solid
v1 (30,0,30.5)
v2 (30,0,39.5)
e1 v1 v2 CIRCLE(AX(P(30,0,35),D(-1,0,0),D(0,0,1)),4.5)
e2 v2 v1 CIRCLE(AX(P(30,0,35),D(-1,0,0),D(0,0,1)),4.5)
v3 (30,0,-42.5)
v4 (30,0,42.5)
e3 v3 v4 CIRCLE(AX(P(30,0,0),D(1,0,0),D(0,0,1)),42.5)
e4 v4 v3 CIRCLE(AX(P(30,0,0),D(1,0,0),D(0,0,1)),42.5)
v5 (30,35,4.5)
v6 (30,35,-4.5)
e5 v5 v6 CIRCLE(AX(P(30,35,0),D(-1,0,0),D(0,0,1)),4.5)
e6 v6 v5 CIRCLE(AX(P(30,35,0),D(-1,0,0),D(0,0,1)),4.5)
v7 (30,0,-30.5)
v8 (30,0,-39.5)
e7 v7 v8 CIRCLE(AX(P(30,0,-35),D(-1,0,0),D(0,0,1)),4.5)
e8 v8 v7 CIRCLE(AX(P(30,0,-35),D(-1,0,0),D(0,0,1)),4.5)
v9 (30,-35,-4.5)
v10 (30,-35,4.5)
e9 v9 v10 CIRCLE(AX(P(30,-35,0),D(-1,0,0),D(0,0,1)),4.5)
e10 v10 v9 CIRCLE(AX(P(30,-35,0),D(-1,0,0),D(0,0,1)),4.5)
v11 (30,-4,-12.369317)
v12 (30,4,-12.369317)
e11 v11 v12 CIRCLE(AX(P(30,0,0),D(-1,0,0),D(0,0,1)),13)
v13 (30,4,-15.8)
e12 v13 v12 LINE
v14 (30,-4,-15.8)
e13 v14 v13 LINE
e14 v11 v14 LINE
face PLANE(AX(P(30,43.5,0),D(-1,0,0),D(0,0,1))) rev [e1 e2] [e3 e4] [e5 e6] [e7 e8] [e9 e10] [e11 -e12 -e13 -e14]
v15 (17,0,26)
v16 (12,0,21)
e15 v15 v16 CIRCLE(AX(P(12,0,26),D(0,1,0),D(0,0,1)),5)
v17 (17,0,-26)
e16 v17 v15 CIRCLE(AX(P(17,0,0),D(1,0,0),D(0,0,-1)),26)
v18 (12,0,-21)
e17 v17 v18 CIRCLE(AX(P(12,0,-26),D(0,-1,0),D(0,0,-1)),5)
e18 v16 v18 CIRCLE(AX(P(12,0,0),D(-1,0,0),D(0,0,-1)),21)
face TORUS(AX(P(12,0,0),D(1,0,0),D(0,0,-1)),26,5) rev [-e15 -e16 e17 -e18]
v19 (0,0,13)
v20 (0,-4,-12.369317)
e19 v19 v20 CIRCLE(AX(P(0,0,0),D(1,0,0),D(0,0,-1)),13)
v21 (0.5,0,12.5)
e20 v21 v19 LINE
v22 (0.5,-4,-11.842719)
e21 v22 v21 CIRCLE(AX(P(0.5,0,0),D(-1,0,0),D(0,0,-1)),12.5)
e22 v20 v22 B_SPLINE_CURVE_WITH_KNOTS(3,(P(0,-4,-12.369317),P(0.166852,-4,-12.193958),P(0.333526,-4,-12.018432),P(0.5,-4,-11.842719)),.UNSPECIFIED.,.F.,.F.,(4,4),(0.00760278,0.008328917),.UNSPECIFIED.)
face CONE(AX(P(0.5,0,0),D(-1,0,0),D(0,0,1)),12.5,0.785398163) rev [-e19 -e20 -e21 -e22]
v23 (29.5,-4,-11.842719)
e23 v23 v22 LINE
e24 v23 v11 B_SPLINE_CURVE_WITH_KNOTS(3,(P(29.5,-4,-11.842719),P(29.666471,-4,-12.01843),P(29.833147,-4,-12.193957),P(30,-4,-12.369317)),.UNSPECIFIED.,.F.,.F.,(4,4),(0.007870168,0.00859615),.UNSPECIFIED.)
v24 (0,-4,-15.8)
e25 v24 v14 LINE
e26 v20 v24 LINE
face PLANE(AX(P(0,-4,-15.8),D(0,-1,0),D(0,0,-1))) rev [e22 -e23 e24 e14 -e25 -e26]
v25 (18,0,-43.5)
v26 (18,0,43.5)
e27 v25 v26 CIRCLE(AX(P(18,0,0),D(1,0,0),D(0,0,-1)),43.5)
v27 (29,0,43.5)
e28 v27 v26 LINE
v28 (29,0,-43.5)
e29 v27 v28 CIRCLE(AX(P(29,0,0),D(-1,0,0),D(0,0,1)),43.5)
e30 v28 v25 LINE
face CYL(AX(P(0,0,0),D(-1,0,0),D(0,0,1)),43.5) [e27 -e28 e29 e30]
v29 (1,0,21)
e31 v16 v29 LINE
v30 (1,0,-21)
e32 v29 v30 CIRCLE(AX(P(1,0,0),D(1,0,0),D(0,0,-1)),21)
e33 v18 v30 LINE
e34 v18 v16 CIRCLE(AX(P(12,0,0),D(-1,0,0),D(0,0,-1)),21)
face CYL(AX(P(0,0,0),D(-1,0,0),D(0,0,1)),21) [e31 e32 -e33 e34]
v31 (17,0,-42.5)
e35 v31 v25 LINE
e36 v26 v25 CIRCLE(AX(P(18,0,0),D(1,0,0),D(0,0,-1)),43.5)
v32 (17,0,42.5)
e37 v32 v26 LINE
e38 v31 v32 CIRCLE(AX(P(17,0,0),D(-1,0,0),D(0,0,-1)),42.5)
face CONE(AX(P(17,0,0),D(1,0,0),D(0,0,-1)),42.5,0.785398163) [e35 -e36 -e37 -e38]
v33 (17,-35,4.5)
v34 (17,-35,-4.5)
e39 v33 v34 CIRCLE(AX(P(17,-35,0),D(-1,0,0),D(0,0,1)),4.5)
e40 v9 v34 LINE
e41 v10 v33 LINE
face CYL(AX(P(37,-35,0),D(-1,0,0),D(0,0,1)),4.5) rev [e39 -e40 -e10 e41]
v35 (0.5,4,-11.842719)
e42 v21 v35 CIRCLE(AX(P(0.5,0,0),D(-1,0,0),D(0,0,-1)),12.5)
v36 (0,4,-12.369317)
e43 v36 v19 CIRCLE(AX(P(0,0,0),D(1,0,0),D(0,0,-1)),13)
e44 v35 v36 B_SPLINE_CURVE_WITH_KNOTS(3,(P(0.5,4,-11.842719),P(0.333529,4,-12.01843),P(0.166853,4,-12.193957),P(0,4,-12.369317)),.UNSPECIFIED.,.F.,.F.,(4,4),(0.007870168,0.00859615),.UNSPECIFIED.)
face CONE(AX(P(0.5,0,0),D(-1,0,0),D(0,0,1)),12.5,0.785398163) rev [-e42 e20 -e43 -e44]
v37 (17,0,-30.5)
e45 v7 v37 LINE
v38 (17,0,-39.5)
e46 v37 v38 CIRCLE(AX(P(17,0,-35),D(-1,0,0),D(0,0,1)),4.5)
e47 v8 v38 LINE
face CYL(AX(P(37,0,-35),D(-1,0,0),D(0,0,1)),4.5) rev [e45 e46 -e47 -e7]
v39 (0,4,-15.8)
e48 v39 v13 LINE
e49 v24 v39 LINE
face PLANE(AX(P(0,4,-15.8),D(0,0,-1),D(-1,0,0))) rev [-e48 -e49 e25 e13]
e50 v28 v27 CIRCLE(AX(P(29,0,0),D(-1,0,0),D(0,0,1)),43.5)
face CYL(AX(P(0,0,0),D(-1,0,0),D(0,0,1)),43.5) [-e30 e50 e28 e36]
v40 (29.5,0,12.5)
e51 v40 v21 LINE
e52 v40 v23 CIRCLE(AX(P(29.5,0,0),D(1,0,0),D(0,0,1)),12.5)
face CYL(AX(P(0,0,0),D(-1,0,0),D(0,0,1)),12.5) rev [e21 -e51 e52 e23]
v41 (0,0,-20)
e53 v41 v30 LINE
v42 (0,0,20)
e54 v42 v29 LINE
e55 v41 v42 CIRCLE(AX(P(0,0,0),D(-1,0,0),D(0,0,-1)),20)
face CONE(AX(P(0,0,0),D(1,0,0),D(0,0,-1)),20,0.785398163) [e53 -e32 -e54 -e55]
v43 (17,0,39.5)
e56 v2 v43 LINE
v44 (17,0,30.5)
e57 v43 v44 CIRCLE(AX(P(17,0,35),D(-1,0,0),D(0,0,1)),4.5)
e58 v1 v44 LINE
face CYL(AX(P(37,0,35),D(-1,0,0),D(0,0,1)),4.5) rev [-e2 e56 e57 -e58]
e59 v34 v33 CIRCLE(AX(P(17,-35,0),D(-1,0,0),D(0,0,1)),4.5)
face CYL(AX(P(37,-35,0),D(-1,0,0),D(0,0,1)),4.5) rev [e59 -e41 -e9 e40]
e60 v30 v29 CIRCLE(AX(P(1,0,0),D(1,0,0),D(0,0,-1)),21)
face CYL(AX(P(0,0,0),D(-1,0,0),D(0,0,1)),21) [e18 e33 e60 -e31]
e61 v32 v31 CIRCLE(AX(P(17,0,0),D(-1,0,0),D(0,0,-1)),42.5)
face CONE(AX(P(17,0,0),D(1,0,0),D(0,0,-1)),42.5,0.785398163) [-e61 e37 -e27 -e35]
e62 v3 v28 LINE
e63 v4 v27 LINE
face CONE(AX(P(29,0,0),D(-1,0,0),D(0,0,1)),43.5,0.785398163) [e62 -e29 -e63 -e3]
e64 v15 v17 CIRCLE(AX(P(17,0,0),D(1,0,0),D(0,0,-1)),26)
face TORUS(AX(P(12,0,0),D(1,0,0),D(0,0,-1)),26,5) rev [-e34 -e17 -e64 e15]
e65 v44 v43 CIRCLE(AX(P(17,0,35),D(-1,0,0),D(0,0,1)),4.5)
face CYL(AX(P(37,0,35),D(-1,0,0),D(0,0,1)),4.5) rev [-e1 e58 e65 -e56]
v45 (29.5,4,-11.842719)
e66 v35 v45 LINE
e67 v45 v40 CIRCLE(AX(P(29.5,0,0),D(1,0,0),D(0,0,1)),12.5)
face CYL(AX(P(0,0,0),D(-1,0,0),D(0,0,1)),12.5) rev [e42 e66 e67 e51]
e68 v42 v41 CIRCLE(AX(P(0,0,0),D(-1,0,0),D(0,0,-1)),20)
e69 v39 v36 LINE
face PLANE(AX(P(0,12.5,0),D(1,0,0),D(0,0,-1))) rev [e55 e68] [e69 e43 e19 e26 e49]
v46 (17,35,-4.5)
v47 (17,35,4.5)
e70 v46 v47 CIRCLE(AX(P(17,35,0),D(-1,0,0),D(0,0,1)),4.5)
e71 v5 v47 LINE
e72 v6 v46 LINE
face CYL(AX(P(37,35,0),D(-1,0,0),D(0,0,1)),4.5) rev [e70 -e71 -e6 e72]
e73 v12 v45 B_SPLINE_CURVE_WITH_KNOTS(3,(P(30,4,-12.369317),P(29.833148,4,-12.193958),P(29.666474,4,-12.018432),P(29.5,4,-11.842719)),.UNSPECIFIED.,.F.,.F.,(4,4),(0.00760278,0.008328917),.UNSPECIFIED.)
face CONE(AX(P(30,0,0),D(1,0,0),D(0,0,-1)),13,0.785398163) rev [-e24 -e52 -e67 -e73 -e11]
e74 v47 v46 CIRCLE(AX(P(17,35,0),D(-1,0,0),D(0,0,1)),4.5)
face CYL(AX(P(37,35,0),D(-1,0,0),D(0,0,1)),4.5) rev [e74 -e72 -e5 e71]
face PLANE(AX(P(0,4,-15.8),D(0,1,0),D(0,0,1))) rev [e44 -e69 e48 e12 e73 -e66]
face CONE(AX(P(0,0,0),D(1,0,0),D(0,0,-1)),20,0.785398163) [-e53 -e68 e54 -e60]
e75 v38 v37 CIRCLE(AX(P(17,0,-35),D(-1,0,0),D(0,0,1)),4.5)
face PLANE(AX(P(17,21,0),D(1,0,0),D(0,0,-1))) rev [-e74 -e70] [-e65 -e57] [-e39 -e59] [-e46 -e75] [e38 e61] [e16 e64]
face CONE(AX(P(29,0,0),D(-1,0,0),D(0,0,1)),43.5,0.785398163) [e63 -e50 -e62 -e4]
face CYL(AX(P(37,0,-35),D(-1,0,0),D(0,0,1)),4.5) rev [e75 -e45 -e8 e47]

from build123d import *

# Parameters (mm, degrees)
CHAMFER1_SIZE      = 1
CHAMFER2_SIZE      = 0.5
FILLET1_R          = 5
CHAMFER3_SIZE      = 1
SKETCH2_R          = 4.5
CUT_EXTRUDE1_DEPTH = 20
SKETCH3_W          = 8.058064516
SKETCH3_H          = 8
CUT_EXTRUDE2_DEPTH = 69.443407279


with BuildPart() as part:
    # Sketch1 → Revolve1 (revolve)
    with BuildSketch(Plane.XY, mode=Mode.PRIVATE) as revolve1_sk:
        Polygon((0, 12.5), (0, 21), (17, 21), (17, 43.5), (30, 43.5), (30, 12.5), align=None)
    revolve(revolve1_sk.sketch.rotate(Axis((0, 0, 0), (1, 0, 0)), 90), axis=Axis((0, 0, 0), (1, 0, 0)))

    # Chamfer1
    chamfer1_edges = [part.edges().sort_by_distance(p)[0] for p in [
        (0, 0, -21),
    ]]
    chamfer(chamfer1_edges, length=CHAMFER1_SIZE)

    # Chamfer2
    chamfer2_edges = [part.edges().sort_by_distance(p)[0] for p in [
        (30, 0, -12.5),
        (0, 0, -12.5),
    ]]
    chamfer(chamfer2_edges, length=CHAMFER2_SIZE)

    # Fillet1
    fillet1_edges = [part.edges().sort_by_distance(p)[0] for p in [
        (17, 0, -21),
    ]]
    fillet(fillet1_edges, radius=FILLET1_R)

    # Chamfer3
    chamfer3_edges = [part.edges().sort_by_distance(p)[0] for p in [
        (17, 0, -43.5),
        (30, 0, -43.5),
    ]]
    chamfer(chamfer3_edges, length=CHAMFER3_SIZE)

    # Sketch2 → Cut-Extrude1 (cut)
    with BuildSketch(Plane.ZY.offset(-17)):
        with Locations((-35, 0)):
            Circle(SKETCH2_R)
        with Locations((0, -35)):
            Circle(SKETCH2_R)
        with Locations((0, 35)):
            Circle(SKETCH2_R)
        with Locations((35, 0)):
            Circle(SKETCH2_R)
    extrude(amount=-CUT_EXTRUDE1_DEPTH, mode=Mode.SUBTRACT)

    # Sketch3 → Cut-Extrude2 (cut, through all)
    with BuildSketch(Plane(origin=(30, 0, 0), x_dir=(0, 0, -1), z_dir=(1, 0, 0))):
        with Locations((11.770967742, 0)):
            Rectangle(SKETCH3_W, SKETCH3_H)
    extrude(amount=-CUT_EXTRUDE2_DEPTH, mode=Mode.SUBTRACT)


solid = part.part
